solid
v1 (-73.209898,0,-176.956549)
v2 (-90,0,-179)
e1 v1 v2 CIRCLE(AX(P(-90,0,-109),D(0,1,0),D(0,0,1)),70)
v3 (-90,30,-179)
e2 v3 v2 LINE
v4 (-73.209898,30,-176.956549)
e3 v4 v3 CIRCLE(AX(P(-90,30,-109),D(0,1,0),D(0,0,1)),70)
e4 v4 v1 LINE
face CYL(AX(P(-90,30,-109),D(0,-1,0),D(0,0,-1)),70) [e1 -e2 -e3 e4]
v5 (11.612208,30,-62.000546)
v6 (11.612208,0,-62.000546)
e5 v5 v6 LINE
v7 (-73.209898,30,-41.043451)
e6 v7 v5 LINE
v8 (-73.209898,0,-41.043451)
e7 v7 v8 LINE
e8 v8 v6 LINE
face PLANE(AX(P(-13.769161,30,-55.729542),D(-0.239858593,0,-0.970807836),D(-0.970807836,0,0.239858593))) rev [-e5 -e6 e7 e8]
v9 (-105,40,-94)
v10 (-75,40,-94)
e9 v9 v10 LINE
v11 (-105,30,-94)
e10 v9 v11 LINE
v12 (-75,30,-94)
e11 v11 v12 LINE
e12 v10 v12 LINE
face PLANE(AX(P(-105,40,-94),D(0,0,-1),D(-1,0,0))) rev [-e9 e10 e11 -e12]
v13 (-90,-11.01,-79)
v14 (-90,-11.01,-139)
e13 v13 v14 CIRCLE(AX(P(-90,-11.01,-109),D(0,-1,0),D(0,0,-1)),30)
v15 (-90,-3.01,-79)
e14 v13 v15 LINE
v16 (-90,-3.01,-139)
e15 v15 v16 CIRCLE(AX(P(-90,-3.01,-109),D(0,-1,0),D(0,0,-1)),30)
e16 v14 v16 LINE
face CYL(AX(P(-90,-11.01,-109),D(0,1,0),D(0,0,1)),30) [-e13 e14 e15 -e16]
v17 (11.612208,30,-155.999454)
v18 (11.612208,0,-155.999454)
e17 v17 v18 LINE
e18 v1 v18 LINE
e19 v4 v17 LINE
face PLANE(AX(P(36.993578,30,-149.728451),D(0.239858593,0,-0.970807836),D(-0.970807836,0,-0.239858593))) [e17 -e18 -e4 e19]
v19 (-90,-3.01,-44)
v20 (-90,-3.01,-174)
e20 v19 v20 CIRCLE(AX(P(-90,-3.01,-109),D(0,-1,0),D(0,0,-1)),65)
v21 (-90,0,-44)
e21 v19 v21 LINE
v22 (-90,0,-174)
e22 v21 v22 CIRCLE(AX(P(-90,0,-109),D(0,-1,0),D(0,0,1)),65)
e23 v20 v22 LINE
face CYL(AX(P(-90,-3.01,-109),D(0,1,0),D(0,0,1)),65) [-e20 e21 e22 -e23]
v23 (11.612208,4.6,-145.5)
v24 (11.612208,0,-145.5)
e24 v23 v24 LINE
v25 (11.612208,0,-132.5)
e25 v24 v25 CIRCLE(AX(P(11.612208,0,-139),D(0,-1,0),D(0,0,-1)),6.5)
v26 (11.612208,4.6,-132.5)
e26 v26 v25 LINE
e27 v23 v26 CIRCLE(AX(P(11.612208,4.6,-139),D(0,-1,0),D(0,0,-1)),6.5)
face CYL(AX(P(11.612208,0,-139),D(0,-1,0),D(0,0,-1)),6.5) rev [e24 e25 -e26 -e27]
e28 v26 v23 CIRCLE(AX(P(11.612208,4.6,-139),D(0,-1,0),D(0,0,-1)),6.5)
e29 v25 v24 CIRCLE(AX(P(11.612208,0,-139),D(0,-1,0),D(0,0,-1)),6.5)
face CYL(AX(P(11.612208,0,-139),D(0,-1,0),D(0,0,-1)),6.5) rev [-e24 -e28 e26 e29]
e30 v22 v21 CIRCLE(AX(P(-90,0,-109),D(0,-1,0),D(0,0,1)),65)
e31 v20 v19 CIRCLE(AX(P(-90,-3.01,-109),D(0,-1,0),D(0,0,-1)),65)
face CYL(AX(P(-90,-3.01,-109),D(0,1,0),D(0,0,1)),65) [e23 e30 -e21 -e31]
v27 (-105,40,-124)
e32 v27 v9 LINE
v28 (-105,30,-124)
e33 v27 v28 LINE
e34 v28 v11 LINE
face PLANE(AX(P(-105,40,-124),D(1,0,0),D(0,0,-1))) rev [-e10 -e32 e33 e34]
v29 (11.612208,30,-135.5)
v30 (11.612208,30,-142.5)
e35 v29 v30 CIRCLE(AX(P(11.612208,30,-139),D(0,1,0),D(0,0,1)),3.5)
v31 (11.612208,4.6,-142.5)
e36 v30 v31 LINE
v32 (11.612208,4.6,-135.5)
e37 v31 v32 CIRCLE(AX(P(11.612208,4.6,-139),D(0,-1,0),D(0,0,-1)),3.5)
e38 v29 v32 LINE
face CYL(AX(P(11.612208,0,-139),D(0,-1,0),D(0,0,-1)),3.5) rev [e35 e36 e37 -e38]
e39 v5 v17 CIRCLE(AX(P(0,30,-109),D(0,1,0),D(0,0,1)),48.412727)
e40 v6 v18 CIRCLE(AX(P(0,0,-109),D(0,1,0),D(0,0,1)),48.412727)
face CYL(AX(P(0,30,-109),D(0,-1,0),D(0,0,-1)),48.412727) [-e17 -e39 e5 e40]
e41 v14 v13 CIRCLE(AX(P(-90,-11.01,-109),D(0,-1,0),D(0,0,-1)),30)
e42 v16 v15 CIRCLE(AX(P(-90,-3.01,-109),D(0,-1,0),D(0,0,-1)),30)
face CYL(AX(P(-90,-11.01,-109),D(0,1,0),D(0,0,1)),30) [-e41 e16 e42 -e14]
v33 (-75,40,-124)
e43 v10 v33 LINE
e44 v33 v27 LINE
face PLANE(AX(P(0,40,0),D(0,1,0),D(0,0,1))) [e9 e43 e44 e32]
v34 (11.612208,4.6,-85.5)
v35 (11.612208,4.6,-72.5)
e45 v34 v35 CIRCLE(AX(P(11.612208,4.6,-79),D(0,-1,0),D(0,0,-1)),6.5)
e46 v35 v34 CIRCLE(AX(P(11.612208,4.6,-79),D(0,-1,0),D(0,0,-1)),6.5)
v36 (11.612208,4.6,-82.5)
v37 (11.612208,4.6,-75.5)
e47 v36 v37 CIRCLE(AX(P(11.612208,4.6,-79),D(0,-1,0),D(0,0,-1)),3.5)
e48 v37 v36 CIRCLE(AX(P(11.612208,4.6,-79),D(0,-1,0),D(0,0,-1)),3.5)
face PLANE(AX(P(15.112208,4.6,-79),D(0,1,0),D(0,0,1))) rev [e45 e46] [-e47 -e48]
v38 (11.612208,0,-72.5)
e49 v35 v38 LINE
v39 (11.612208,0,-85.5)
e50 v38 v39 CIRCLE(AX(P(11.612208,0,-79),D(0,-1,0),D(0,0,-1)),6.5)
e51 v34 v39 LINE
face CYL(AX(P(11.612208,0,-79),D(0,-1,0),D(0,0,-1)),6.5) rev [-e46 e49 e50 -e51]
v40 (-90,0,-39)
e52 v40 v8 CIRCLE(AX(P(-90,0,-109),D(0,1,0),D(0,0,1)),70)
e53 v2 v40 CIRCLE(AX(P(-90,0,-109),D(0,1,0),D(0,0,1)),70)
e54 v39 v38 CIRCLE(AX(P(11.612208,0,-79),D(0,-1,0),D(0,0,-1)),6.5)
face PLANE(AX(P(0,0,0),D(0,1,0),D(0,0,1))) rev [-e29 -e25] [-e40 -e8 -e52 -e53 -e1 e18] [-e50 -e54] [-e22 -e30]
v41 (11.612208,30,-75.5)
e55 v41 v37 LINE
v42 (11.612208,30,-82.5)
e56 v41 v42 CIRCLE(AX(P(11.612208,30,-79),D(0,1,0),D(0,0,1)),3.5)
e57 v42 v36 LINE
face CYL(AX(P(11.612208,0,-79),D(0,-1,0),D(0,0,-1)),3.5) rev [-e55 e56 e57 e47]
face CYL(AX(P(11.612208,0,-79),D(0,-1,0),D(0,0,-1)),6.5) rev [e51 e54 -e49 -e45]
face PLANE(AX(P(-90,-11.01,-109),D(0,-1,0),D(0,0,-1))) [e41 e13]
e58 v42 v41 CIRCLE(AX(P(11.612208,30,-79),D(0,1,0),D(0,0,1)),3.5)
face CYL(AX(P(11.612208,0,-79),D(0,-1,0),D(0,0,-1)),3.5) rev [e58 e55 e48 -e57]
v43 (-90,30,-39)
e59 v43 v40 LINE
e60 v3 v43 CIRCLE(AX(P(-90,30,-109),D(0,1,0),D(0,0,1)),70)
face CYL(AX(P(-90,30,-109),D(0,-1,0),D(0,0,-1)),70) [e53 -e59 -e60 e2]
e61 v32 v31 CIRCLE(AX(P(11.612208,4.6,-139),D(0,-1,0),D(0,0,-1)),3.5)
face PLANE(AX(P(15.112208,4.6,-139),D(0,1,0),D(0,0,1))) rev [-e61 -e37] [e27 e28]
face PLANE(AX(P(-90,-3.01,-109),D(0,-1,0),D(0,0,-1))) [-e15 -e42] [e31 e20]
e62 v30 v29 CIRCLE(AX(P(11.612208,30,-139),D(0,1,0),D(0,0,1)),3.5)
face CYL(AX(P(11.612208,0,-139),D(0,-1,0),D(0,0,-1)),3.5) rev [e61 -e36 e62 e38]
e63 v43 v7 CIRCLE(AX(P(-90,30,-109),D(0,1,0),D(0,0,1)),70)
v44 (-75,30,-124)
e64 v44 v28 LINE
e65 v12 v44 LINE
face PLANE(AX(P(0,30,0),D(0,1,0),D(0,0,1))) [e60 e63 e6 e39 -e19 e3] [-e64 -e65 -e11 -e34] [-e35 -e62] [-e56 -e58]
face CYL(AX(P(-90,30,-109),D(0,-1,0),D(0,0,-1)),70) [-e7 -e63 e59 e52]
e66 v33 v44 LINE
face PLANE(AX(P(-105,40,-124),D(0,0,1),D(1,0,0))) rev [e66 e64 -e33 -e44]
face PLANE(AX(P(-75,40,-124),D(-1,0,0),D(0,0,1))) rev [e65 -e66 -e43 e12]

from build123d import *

# Parameters (mm, degrees)
BOSS_EXTRUDE1_DEPTH                      = 30
SKETCH2_W                                = 30
SKETCH2_H                                = 30
BOSS_EXTRUDE2_DEPTH                      = 10
SKETCH3_R                                = 65
BOSS_EXTRUDE3_DEPTH                      = 3.01
SKETCH4_R                                = 30
BOSS_EXTRUDE4_DEPTH                      = 8
CBORE_FOR_M6_PAN_HEAD_SCREW1_D           = 7
CBORE_FOR_M6_PAN_HEAD_SCREW1_DEPTH       = 50.5
CBORE_FOR_M6_PAN_HEAD_SCREW1_CBORE_D     = 13
CBORE_FOR_M6_PAN_HEAD_SCREW1_CBORE_DEPTH = 4.6
CBORE_FOR_M6_PAN_HEAD_SCREW1_TIP         = 2.103012167


with BuildPart() as part:
    # Sketch1 → Boss-Extrude1 (new body)
    with BuildSketch(Plane(origin=(0, 0, 0), x_dir=(1, 0, 0), z_dir=(0, 1, 0))):
        with BuildLine():
            Line((11.612208492, 155.9994544), (-73.209898492, 176.956548554))
            ThreePointArc((-73.209898492, 176.956548554), (-160, 109), (-73.209898492, 41.043451446))
            Line((-73.209898492, 41.043451446), (11.610000013, 61.999999948))
            Line((11.610000013, 61.999999948), (11.612208492, 62.0005456))
            ThreePointArc((11.612208492, 62.0005456), (48.412726633, 109), (11.612208492, 155.9994544))
        make_face()
    extrude(amount=BOSS_EXTRUDE1_DEPTH)

    # Sketch2 → Boss-Extrude2 (add)
    with BuildSketch(Plane(origin=(0, 30, 0), x_dir=(1, 0, 0), z_dir=(0, 1, 0))):
        with Locations((-90, 109)):
            Rectangle(SKETCH2_W, SKETCH2_H)
    extrude(amount=BOSS_EXTRUDE2_DEPTH)

    # Sketch3 → Boss-Extrude3 (add)
    with BuildSketch(Plane.XZ):
        with Locations(Location((-90, -109, 0), (0, 0, 90))):
            Circle(SKETCH3_R)
    extrude(amount=BOSS_EXTRUDE3_DEPTH)

    # Sketch4 → Boss-Extrude4 (add)
    with BuildSketch(Plane.XZ.offset(3.01)):
        with Locations(Location((-90, -109, 0), (0, 0, 270))):
            Circle(SKETCH4_R)
    extrude(amount=BOSS_EXTRUDE4_DEPTH)

    # CBORE for M6 Pan Head Screw1
    with Locations(Plane(origin=(11.612208492, 0, -79), x_dir=(0, 0, -1), z_dir=(0, -1, 0))):
        with Locations((0, 0), (60, 0)):
            CounterBoreHole(CBORE_FOR_M6_PAN_HEAD_SCREW1_D / 2, CBORE_FOR_M6_PAN_HEAD_SCREW1_CBORE_D / 2, CBORE_FOR_M6_PAN_HEAD_SCREW1_CBORE_DEPTH, depth=CBORE_FOR_M6_PAN_HEAD_SCREW1_DEPTH)
            with Locations((0, 0, -(CBORE_FOR_M6_PAN_HEAD_SCREW1_DEPTH + CBORE_FOR_M6_PAN_HEAD_SCREW1_TIP / 2))):  # 118° drill point
                Cone(0, CBORE_FOR_M6_PAN_HEAD_SCREW1_D / 2, CBORE_FOR_M6_PAN_HEAD_SCREW1_TIP, mode=Mode.SUBTRACT)


solid = part.part
